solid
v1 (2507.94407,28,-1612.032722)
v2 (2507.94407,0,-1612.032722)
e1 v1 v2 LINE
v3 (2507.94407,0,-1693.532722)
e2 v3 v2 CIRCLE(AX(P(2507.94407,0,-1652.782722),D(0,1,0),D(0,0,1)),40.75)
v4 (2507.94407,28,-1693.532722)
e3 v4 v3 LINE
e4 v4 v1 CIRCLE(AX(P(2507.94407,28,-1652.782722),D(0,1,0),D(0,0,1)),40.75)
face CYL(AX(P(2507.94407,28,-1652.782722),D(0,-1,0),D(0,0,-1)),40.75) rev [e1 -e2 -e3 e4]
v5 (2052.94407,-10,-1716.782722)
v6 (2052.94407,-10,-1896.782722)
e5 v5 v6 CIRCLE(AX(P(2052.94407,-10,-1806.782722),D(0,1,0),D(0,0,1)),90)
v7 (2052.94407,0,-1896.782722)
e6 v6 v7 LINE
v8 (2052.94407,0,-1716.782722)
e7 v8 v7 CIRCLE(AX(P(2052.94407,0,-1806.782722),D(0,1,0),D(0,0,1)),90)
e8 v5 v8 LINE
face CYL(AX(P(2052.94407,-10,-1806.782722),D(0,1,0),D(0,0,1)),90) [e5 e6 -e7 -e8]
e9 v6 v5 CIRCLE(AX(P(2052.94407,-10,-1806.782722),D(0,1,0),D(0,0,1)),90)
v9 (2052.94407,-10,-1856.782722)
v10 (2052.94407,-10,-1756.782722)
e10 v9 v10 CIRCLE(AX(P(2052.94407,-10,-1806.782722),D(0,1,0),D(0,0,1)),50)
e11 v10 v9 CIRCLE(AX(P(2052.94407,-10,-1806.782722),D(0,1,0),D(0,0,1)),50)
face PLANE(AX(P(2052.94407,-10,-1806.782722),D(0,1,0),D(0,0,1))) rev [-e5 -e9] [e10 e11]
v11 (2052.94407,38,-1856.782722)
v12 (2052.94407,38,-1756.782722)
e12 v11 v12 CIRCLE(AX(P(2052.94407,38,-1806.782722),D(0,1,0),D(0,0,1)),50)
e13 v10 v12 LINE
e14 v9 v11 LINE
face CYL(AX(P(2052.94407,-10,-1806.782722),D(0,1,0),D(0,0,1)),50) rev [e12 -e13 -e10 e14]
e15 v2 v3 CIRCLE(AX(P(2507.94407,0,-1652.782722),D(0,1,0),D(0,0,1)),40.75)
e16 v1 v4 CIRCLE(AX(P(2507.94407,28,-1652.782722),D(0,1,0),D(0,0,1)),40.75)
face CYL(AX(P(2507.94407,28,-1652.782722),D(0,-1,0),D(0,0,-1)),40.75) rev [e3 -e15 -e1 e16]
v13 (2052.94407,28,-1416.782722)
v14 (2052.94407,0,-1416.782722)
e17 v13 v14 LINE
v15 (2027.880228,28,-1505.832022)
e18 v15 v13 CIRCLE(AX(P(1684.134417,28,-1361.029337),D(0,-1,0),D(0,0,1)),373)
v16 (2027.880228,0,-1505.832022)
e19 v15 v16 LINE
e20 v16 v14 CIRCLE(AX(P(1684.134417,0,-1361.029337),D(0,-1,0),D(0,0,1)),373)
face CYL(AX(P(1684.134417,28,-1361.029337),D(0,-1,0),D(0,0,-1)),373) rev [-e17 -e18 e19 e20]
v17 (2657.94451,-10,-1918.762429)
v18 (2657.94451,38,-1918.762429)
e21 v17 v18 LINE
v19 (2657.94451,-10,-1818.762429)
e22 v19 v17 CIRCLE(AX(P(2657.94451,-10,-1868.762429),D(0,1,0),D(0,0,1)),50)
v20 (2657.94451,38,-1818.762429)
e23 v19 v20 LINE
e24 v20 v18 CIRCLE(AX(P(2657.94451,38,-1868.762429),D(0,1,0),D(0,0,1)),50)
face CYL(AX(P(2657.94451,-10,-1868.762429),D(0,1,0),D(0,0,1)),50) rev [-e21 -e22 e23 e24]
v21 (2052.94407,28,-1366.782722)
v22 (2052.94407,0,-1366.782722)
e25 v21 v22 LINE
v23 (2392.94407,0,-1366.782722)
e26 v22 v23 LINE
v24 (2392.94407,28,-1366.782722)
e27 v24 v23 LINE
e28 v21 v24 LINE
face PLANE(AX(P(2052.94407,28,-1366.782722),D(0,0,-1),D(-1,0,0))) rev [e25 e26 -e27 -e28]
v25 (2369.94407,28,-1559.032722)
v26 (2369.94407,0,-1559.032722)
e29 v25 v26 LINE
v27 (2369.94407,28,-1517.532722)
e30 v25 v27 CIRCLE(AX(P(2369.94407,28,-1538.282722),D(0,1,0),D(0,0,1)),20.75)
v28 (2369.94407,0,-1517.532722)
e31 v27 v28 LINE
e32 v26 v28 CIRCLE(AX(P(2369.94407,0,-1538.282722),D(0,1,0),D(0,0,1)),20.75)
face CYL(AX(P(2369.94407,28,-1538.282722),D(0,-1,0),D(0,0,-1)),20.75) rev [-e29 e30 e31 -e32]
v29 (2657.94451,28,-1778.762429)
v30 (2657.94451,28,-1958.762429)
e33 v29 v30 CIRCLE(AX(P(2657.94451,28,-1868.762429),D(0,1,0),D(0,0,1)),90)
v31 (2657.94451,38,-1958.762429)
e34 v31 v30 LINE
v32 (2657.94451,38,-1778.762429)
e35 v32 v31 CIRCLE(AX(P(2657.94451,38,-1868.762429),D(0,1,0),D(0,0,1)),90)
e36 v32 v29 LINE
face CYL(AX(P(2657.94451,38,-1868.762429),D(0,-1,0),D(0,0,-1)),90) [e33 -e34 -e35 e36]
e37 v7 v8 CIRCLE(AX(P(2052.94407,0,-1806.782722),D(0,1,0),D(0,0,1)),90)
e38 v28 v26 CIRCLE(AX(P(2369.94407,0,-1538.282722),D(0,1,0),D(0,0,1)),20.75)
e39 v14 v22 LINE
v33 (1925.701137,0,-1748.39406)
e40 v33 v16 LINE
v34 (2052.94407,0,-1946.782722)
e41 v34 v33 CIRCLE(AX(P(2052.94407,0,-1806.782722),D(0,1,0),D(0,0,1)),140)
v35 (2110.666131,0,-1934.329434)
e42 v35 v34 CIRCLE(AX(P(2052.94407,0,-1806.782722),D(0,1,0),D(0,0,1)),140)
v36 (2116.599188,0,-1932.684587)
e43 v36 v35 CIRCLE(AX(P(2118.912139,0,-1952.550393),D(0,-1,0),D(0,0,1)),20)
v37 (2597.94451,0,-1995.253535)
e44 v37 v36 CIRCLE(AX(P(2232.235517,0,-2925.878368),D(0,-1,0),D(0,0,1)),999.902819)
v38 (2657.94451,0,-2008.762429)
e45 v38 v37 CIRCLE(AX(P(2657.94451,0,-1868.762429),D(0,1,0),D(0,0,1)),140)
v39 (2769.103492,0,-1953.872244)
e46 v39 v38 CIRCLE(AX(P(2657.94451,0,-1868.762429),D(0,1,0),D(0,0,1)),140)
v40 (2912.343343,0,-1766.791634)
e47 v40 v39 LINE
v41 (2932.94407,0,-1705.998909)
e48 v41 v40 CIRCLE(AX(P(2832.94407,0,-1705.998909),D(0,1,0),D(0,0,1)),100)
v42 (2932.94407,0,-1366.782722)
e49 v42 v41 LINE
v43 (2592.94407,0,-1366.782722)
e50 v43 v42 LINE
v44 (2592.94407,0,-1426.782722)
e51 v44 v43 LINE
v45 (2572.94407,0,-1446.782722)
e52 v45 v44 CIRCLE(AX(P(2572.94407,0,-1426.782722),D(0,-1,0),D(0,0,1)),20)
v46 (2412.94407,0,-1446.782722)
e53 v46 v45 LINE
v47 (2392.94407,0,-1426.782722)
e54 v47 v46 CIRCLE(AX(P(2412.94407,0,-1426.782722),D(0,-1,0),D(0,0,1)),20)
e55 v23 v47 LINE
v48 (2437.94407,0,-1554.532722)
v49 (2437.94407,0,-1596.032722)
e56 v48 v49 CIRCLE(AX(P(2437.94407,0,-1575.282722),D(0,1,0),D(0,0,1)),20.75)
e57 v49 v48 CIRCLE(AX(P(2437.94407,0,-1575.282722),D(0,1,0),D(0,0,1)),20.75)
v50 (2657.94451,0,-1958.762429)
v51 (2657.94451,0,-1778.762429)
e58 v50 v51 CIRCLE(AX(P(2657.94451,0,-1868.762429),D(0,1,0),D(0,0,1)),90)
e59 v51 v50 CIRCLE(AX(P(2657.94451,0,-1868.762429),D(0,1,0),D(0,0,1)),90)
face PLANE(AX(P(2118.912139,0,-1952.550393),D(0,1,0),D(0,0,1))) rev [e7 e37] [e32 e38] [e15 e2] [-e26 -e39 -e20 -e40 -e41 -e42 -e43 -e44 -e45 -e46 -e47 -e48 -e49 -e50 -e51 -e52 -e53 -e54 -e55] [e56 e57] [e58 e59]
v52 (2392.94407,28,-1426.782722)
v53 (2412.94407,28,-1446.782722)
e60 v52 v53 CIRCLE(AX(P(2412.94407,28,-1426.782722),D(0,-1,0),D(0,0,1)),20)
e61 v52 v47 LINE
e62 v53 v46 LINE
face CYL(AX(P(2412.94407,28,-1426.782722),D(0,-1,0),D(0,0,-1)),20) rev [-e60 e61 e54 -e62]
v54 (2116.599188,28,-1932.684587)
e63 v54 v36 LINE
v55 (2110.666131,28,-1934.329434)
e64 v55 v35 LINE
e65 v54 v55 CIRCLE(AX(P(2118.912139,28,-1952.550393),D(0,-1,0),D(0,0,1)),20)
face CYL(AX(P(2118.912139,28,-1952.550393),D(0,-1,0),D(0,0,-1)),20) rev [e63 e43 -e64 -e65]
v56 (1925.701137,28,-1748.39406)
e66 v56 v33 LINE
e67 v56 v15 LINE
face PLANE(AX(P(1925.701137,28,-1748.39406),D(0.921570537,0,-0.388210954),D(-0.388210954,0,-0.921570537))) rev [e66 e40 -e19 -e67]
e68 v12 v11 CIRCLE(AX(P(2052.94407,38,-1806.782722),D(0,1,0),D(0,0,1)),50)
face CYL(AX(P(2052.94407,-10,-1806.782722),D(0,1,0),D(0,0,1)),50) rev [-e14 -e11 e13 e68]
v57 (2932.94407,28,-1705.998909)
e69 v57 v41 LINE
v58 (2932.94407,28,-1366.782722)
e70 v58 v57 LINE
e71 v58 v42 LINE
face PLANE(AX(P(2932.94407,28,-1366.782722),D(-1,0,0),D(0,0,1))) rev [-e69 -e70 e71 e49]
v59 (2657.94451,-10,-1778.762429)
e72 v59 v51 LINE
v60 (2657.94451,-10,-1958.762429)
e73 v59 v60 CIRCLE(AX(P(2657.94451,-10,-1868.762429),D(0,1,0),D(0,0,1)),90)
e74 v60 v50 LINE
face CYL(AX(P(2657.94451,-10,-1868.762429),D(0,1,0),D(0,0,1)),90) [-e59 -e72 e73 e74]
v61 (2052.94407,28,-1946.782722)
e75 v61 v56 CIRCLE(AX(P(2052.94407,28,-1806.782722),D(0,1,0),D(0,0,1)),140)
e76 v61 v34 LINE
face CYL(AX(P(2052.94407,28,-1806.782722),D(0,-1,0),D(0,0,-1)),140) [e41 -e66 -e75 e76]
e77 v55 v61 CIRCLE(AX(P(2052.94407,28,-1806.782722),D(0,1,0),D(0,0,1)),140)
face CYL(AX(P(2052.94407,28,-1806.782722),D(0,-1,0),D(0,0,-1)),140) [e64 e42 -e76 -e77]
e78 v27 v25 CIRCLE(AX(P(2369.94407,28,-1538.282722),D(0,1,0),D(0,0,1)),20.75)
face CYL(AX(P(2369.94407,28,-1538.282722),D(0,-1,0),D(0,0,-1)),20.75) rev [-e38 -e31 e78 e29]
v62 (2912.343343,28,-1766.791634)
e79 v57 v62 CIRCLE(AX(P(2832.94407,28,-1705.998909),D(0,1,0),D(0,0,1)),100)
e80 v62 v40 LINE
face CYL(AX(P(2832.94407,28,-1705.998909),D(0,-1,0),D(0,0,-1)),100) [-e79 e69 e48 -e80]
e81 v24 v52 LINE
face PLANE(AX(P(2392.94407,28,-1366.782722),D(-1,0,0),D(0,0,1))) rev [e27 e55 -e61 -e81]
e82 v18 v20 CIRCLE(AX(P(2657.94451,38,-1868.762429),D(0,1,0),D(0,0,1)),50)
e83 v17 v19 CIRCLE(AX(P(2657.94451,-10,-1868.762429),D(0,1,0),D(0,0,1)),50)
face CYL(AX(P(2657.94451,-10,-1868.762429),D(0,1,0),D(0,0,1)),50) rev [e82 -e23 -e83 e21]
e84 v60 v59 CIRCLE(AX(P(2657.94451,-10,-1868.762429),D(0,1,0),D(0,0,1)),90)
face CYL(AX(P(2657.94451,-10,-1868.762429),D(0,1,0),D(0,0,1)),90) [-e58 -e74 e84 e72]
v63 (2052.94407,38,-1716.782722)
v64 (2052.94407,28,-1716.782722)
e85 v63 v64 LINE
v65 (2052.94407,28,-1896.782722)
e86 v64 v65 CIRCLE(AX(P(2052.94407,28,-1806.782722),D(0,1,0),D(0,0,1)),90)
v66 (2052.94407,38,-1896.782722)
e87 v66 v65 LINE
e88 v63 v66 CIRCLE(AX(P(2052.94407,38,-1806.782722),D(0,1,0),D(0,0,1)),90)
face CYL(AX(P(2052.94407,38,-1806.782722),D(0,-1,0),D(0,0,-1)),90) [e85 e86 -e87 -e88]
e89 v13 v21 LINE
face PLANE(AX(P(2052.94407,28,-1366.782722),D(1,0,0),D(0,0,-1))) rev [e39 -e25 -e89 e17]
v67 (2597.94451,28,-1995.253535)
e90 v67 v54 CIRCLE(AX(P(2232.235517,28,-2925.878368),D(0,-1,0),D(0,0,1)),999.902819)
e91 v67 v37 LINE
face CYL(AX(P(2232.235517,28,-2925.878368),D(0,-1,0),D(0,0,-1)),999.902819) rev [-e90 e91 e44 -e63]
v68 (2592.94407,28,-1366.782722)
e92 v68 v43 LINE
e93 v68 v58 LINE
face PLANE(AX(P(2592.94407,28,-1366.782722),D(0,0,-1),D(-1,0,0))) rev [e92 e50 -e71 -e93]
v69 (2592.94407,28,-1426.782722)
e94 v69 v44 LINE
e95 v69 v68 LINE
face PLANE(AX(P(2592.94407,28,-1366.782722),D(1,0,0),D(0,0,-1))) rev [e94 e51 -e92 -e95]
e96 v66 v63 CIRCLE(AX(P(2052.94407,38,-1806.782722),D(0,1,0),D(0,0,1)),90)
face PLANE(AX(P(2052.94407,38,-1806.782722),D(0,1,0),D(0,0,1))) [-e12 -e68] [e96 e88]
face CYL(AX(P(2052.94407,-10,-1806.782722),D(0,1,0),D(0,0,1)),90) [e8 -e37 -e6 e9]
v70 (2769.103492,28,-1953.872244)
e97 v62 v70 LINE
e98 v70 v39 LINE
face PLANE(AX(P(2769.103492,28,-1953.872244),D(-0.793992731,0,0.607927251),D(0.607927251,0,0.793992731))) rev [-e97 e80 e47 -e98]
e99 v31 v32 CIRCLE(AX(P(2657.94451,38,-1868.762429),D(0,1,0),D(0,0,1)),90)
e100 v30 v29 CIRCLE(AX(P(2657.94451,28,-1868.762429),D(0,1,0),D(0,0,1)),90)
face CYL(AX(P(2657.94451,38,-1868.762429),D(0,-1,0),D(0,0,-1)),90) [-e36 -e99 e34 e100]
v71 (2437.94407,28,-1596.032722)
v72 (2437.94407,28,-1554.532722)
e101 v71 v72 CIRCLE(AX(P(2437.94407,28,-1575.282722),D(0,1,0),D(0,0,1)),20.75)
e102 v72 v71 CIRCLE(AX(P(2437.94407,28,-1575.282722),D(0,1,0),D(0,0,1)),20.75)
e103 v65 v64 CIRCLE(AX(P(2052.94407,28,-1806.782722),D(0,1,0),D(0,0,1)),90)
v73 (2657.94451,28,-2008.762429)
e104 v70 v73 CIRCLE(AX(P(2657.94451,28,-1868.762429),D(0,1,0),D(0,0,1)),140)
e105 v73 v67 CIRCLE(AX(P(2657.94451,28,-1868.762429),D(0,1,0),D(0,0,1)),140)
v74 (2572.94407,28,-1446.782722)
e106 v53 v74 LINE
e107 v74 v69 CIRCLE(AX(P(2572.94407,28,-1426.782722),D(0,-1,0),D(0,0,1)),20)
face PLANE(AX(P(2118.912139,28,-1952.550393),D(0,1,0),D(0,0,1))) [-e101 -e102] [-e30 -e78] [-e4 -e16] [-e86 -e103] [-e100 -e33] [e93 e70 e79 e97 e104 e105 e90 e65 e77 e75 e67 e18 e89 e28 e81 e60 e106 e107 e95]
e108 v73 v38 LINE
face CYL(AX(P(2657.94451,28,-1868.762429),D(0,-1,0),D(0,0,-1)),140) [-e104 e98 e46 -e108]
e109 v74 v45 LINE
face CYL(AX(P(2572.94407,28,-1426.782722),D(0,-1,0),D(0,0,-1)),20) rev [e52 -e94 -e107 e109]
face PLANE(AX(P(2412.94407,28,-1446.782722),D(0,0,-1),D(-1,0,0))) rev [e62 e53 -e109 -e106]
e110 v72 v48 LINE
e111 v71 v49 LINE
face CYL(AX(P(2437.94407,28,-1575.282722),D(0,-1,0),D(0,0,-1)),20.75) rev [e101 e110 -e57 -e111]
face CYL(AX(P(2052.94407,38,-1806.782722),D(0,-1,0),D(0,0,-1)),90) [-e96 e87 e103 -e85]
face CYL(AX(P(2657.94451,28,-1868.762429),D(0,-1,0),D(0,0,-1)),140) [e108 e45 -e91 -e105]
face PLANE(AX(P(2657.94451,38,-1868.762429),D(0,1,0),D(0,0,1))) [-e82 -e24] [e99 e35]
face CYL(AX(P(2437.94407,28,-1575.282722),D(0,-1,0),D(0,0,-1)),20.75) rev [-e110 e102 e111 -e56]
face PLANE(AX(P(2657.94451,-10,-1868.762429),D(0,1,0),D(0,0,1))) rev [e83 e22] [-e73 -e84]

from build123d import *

# Parameters (mm, degrees)
SKETCH1_R             = 20.75
SKETCH1_R_2           = 90
SKETCH1_R_3           = 40.75
BOSS_EXTRUDE1_DEPTH   = 28
SKETCH_2_2_R          = 90
SKETCH_2_2_R_2        = 50
BOSS_EXTRUDE2_DEPTH   = 10
BOSS_EXTRUDE2_2_DEPTH = 10
BOSS_EXTRUDE3_START   = -38
SKETCH_2_2_2_R        = 90
SKETCH_2_2_2_R_2      = 50
BOSS_EXTRUDE3_DEPTH   = 38


with BuildPart() as part:
    # Sketch1 → Boss-Extrude1 (new body)
    with BuildSketch(Plane(origin=(0, 0, 0), x_dir=(1, 0, 0), z_dir=(0, 1, 0))):
        with BuildLine():
            Line((1925.70113656, 1748.394060435), (2027.880227878, 1505.832022369))
            ThreePointArc((2027.880227878, 1505.832022369), (2043.18353175, 1462.087406566), (2052.944070187, 1416.782722365))
            Line((2052.944070187, 1416.782722365), (2052.944070187, 1366.782722365))
            Line((2052.944070187, 1366.782722365), (2392.944070187, 1366.782722365))
            Line((2392.944070187, 1366.782722365), (2392.944070187, 1426.782722365))
            ThreePointArc((2392.944070187, 1426.782722365), (2398.801934564, 1440.924857989), (2412.944070187, 1446.782722365))
            Line((2412.944070187, 1446.782722365), (2572.944070187, 1446.782722365))
            ThreePointArc((2572.944070187, 1446.782722365), (2587.086205811, 1440.924857989), (2592.944070187, 1426.782722365))
            Line((2592.944070187, 1426.782722365), (2592.944070187, 1366.782722365))
            Line((2592.944070187, 1366.782722365), (2932.944070187, 1366.782722365))
            Line((2932.944070187, 1366.782722365), (2932.944070187, 1705.998908982))
            ThreePointArc((2932.944070187, 1705.998908982), (2927.653962259, 1738.093088264), (2912.343343312, 1766.791634101))
            Line((2912.343343312, 1766.791634101), (2769.10349201, 1953.872243723))
            ThreePointArc((2769.10349201, 1953.872243723), (2690.844558049, 2004.841768703), (2597.944509636, 1995.253534964))
            ThreePointArc((2597.944509636, 1995.253534964), (2361.126178322, 1934.317555647), (2116.599187921, 1932.684586999))
            ThreePointArc((2116.599187921, 1932.684586999), (2113.568985738, 1933.277336612), (2110.666130639, 1934.329434346))
            ThreePointArc((2110.666130639, 1934.329434346), (1953.690461842, 1905.518335141), (1925.70113656, 1748.394060435))
        make_face()
        with Locations(Location((2369.944070187, 1538.282722365, 0), (0, 0, 270))):
            Circle(SKETCH1_R, mode=Mode.SUBTRACT)
        with Locations(Location((2437.944070187, 1575.282722365, 0), (0, 0, 270))):
            Circle(SKETCH1_R, mode=Mode.SUBTRACT)
        with Locations(Location((2052.944070187, 1806.782722365, 0), (0, 0, 270))):
            Circle(SKETCH1_R_2, mode=Mode.SUBTRACT)
        with Locations(Location((2657.944509636, 1868.762428557, 0), (0, 0, 270))):
            Circle(SKETCH1_R_2, mode=Mode.SUBTRACT)
        with Locations(Location((2507.944070187, 1652.782722365, 0), (0, 0, 270))):
            Circle(SKETCH1_R_3, mode=Mode.SUBTRACT)
    extrude(amount=BOSS_EXTRUDE1_DEPTH)



with BuildPart() as body_2:
    # Sketch 2_2 → Boss-Extrude2 (new body)
    with BuildSketch(Plane(origin=(0, 28, 0), x_dir=(1, 0, 0), z_dir=(0, 1, 0))):
        with Locations(Location((2052.944070187, 1806.782722365, 0), (0, 0, 270))):
            Circle(SKETCH_2_2_R)
        with Locations(Location((2052.944070187, 1806.782722365, 0), (0, 0, 270))):
            Circle(SKETCH_2_2_R_2, mode=Mode.SUBTRACT)
    extrude(amount=BOSS_EXTRUDE2_DEPTH)


with BuildPart() as body_3:
    # Sketch 2_2 → Boss-Extrude2 2 (new body)
    with BuildSketch(Plane(origin=(0, 28, 0), x_dir=(1, 0, 0), z_dir=(0, 1, 0))):
        with Locations(Location((2657.944509636, 1868.762428557, 0), (0, 0, 270))):
            Circle(SKETCH_2_2_R)
        with Locations(Location((2657.944509636, 1868.762428557, 0), (0, 0, 270))):
            Circle(SKETCH_2_2_R_2, mode=Mode.SUBTRACT)
    extrude(amount=BOSS_EXTRUDE2_2_DEPTH)


with BuildPart() as part_1:
    add(part.part)

    add(body_2.part)  # Boss-Extrude3 merges body 2

    add(body_3.part)  # Boss-Extrude3 merges body 3
    # Sketch 2_2 2 → Boss-Extrude3 (add)
    # profile 1 of 2: a face of its own
    with BuildSketch(Plane(origin=(0, 28, 0), x_dir=(1, 0, 0), z_dir=(0, 1, 0)).offset(BOSS_EXTRUDE3_START)):
        with Locations(Location((2052.944070187, 1806.782722365, 0), (0, 0, 270))):
            Circle(SKETCH_2_2_2_R)
        with Locations(Location((2052.944070187, 1806.782722365, 0), (0, 0, 270))):
            Circle(SKETCH_2_2_2_R_2, mode=Mode.SUBTRACT)
    # profile 2 of 2: a face of its own
    with BuildSketch(Plane(origin=(0, 28, 0), x_dir=(1, 0, 0), z_dir=(0, 1, 0)).offset(BOSS_EXTRUDE3_START)):
        with Locations(Location((2657.944509636, 1868.762428557, 0), (0, 0, 270))):
            Circle(SKETCH_2_2_2_R)
        with Locations(Location((2657.944509636, 1868.762428557, 0), (0, 0, 270))):
            Circle(SKETCH_2_2_2_R_2, mode=Mode.SUBTRACT)
    extrude(amount=BOSS_EXTRUDE3_DEPTH)


solid = part_1.part
